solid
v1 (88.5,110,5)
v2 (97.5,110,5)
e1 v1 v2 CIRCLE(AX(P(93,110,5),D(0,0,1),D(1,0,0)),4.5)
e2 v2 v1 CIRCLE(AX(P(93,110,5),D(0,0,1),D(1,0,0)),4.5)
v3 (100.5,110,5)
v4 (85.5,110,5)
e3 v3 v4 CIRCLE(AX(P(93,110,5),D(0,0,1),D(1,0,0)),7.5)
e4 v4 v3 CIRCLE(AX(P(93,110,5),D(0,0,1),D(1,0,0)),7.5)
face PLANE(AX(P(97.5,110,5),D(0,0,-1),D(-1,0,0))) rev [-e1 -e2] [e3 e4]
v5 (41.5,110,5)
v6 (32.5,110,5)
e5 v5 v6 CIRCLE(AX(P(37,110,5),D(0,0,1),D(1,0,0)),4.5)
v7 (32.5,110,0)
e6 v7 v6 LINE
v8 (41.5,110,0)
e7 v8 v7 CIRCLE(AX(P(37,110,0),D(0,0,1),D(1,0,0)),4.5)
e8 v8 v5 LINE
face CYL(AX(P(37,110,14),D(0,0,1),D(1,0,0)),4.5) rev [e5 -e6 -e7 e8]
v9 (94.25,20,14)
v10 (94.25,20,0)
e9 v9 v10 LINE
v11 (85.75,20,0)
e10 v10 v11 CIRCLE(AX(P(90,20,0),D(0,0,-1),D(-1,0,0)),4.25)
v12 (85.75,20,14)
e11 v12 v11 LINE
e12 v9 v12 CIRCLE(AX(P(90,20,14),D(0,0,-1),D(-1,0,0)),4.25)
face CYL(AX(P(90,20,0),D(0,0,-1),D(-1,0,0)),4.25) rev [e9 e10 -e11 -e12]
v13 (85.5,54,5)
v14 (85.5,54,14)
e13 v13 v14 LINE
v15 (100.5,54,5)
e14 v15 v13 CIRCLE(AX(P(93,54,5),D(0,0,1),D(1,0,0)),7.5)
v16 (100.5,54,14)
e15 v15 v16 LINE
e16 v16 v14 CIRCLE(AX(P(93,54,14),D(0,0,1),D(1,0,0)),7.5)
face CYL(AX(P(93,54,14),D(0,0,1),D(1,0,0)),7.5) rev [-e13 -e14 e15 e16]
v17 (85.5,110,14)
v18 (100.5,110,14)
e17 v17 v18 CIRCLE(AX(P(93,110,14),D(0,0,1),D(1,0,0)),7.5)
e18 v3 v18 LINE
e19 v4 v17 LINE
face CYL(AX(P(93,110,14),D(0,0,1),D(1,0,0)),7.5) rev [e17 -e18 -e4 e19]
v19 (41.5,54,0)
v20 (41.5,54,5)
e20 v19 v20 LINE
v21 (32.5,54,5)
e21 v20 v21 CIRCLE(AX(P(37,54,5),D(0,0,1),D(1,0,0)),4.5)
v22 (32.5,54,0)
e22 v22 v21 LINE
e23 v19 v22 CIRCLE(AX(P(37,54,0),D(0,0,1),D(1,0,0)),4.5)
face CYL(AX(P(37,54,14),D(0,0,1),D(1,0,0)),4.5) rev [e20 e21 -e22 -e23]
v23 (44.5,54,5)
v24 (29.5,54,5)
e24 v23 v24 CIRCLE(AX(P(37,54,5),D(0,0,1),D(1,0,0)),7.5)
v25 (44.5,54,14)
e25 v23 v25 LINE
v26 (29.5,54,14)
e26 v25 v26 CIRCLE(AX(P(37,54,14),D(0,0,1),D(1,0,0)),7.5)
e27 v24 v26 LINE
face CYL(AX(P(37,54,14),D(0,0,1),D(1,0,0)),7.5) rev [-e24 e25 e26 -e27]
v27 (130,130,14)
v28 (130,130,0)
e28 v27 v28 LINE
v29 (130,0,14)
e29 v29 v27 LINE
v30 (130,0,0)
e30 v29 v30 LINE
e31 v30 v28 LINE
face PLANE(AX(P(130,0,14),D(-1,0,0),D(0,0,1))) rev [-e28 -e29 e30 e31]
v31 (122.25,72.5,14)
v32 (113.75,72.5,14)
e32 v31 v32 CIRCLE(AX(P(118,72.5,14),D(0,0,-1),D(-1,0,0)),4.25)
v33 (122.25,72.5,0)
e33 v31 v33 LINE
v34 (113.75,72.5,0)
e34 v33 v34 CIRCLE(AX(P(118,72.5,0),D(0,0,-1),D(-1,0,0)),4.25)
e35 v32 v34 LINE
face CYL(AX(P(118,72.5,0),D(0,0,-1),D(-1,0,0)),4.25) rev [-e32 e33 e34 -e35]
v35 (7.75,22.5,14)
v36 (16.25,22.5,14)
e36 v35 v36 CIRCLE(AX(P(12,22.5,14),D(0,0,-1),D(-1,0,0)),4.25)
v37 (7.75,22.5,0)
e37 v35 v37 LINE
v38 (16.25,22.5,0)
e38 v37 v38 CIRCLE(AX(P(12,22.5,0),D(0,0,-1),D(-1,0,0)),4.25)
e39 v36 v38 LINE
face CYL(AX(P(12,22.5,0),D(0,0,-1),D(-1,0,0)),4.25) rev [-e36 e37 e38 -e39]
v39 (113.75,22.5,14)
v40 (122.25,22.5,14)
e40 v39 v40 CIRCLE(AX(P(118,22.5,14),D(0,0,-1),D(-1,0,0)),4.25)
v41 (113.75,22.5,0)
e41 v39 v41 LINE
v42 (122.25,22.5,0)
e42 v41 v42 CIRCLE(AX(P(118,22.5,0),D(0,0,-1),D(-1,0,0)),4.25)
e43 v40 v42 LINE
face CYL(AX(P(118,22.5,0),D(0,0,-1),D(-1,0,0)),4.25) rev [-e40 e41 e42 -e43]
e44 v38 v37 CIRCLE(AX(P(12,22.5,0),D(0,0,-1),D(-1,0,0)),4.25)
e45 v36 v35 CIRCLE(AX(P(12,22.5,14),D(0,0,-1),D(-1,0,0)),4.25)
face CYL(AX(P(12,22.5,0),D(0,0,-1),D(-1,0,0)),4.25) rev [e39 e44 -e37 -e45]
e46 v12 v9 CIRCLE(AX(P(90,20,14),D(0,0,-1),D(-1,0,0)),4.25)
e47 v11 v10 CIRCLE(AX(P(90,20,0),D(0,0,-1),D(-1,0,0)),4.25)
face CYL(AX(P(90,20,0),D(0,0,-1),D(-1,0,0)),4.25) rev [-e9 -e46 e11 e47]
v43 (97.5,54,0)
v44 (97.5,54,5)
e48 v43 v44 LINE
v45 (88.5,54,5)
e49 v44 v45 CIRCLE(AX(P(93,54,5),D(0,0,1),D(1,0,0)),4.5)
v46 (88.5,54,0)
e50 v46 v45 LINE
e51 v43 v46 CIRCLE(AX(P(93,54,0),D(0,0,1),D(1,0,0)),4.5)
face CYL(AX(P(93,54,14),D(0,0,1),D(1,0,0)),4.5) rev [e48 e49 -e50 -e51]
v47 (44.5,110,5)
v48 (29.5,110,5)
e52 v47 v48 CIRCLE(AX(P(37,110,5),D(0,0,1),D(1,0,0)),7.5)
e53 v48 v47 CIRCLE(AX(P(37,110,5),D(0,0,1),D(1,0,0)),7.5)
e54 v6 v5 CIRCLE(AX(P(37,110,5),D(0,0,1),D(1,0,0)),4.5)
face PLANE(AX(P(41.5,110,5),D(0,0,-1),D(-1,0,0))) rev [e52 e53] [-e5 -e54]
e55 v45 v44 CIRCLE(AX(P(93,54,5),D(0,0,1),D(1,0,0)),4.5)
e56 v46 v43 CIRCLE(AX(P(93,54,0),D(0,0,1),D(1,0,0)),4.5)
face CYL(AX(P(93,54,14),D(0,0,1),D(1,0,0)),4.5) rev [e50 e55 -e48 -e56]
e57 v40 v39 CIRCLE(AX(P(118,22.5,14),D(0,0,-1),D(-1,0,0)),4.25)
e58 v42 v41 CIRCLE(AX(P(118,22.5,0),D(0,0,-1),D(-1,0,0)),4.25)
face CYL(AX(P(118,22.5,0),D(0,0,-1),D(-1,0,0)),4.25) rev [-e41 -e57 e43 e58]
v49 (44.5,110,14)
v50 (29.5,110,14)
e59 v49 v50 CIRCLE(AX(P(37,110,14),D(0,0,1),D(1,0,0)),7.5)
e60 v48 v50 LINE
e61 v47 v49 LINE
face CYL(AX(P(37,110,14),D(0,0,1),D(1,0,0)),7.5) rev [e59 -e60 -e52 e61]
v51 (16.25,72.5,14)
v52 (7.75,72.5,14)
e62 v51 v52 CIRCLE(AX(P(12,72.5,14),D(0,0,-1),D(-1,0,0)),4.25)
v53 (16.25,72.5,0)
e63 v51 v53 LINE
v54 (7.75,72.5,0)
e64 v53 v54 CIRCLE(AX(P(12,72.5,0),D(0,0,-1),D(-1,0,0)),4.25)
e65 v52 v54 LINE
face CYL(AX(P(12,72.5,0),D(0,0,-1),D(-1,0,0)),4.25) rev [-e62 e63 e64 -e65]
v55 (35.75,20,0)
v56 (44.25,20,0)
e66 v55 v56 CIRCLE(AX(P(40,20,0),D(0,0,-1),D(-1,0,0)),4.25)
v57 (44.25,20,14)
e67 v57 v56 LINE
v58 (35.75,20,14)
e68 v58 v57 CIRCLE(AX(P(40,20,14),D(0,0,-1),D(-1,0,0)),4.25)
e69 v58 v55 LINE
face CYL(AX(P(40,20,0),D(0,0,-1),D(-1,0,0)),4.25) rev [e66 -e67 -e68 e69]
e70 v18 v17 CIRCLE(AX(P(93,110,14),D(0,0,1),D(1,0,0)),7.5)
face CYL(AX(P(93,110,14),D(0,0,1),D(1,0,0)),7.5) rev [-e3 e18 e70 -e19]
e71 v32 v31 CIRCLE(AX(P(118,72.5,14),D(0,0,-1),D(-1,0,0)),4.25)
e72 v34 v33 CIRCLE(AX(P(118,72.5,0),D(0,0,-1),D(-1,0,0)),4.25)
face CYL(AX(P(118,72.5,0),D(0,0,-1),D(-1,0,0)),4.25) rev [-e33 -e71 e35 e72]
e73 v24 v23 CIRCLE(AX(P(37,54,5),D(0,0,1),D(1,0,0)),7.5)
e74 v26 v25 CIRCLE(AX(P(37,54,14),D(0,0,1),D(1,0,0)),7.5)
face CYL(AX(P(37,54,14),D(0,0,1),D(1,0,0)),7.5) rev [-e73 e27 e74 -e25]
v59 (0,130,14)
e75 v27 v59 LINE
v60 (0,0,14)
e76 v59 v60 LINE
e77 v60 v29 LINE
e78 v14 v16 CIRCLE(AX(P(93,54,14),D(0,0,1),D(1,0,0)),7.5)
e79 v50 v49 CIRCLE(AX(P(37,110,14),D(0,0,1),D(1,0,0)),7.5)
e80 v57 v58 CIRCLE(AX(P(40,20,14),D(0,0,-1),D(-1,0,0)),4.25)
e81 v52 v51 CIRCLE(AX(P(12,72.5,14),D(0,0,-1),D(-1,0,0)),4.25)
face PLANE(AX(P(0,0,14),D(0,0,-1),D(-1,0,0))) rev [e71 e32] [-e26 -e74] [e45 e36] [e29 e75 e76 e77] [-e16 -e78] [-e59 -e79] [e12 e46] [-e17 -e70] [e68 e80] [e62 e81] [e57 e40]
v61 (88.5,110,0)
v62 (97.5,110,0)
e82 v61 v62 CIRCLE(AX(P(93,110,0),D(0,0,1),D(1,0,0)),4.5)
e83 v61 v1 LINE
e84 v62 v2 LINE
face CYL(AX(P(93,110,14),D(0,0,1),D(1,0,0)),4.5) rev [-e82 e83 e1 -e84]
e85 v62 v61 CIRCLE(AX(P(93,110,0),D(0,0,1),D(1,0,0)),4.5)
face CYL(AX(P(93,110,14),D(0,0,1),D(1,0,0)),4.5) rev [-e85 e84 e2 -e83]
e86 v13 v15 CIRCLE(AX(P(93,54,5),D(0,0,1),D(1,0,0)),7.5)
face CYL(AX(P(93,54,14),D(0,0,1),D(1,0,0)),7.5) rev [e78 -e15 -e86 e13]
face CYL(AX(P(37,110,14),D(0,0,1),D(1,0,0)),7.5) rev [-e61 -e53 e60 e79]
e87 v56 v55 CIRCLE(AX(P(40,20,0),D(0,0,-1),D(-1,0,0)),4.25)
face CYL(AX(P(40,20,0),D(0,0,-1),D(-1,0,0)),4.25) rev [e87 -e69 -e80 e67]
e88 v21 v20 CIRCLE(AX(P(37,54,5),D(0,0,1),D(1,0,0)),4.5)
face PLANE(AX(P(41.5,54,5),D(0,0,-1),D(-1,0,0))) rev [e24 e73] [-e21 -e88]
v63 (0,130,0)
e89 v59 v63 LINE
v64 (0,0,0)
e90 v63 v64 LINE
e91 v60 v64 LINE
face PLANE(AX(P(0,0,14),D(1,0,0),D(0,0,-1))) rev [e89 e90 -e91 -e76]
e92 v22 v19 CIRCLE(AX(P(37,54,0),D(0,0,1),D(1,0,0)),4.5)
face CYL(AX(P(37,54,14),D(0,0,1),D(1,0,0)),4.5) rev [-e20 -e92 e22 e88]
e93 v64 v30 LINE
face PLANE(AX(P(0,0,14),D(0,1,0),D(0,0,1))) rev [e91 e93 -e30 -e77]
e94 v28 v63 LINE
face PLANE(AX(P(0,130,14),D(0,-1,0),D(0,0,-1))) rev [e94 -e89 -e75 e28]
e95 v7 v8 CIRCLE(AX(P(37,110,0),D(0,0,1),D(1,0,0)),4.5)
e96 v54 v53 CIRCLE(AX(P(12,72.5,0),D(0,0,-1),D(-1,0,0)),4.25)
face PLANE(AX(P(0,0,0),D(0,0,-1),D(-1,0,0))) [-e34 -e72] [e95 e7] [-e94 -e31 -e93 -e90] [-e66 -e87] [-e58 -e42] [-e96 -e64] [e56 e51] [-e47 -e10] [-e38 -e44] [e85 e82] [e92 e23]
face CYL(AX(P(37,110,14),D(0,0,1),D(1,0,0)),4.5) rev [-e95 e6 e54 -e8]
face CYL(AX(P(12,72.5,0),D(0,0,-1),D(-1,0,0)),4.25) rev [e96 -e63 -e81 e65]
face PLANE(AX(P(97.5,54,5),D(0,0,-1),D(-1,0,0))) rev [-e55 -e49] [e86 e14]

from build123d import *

# Parameters (mm, degrees)
SKETCH1_W                                          = 130
SKETCH1_H                                          = 130
BOSS_EXTRUDE1_DEPTH                                = 14
HOLE_SIZE_BASED_ON_SOCKET_HEAD_CAP_SCR_D           = 9
HOLE_SIZE_BASED_ON_SOCKET_HEAD_CAP_SCR_CBORE_D     = 15
HOLE_SIZE_BASED_ON_SOCKET_HEAD_CAP_SCR_CBORE_DEPTH = 9
M10_TAPPED_HOLE1_D                                 = 8.5
M10_TAPPED_HOLE2_D                                 = 8.5


with BuildPart() as part:
    # Sketch1 → Boss-Extrude1 (new body)
    with BuildSketch(Plane.XY):
        with Locations((65, 65)):
            Rectangle(SKETCH1_W, SKETCH1_H)
    extrude(amount=BOSS_EXTRUDE1_DEPTH)

    # Hole Size (%based on) Socket Head Cap Screw Type1 (through all)
    with Locations(Plane.XY.offset(14)):
        with Locations((37, 110), (93, 110), (93, 54), (37, 54)):
            CounterBoreHole(HOLE_SIZE_BASED_ON_SOCKET_HEAD_CAP_SCR_D / 2, HOLE_SIZE_BASED_ON_SOCKET_HEAD_CAP_SCR_CBORE_D / 2, HOLE_SIZE_BASED_ON_SOCKET_HEAD_CAP_SCR_CBORE_DEPTH)

    # M10 Tapped Hole1 (through all)
    with Locations(Plane(origin=(0, 0, 0), x_dir=(-1, 0, 0), z_dir=(0, 0, -1))):
        with Locations((-90, 20), (-40, 20)):
            Hole(M10_TAPPED_HOLE1_D / 2)

    # M10 Tapped Hole2 (through all)
    with Locations(Plane(origin=(0, 0, 0), x_dir=(-1, 0, 0), z_dir=(0, 0, -1))):
        with Locations((-118, 72.5), (-118, 22.5), (-12, 72.5), (-12, 22.5)):
            Hole(M10_TAPPED_HOLE2_D / 2)


solid = part.part
